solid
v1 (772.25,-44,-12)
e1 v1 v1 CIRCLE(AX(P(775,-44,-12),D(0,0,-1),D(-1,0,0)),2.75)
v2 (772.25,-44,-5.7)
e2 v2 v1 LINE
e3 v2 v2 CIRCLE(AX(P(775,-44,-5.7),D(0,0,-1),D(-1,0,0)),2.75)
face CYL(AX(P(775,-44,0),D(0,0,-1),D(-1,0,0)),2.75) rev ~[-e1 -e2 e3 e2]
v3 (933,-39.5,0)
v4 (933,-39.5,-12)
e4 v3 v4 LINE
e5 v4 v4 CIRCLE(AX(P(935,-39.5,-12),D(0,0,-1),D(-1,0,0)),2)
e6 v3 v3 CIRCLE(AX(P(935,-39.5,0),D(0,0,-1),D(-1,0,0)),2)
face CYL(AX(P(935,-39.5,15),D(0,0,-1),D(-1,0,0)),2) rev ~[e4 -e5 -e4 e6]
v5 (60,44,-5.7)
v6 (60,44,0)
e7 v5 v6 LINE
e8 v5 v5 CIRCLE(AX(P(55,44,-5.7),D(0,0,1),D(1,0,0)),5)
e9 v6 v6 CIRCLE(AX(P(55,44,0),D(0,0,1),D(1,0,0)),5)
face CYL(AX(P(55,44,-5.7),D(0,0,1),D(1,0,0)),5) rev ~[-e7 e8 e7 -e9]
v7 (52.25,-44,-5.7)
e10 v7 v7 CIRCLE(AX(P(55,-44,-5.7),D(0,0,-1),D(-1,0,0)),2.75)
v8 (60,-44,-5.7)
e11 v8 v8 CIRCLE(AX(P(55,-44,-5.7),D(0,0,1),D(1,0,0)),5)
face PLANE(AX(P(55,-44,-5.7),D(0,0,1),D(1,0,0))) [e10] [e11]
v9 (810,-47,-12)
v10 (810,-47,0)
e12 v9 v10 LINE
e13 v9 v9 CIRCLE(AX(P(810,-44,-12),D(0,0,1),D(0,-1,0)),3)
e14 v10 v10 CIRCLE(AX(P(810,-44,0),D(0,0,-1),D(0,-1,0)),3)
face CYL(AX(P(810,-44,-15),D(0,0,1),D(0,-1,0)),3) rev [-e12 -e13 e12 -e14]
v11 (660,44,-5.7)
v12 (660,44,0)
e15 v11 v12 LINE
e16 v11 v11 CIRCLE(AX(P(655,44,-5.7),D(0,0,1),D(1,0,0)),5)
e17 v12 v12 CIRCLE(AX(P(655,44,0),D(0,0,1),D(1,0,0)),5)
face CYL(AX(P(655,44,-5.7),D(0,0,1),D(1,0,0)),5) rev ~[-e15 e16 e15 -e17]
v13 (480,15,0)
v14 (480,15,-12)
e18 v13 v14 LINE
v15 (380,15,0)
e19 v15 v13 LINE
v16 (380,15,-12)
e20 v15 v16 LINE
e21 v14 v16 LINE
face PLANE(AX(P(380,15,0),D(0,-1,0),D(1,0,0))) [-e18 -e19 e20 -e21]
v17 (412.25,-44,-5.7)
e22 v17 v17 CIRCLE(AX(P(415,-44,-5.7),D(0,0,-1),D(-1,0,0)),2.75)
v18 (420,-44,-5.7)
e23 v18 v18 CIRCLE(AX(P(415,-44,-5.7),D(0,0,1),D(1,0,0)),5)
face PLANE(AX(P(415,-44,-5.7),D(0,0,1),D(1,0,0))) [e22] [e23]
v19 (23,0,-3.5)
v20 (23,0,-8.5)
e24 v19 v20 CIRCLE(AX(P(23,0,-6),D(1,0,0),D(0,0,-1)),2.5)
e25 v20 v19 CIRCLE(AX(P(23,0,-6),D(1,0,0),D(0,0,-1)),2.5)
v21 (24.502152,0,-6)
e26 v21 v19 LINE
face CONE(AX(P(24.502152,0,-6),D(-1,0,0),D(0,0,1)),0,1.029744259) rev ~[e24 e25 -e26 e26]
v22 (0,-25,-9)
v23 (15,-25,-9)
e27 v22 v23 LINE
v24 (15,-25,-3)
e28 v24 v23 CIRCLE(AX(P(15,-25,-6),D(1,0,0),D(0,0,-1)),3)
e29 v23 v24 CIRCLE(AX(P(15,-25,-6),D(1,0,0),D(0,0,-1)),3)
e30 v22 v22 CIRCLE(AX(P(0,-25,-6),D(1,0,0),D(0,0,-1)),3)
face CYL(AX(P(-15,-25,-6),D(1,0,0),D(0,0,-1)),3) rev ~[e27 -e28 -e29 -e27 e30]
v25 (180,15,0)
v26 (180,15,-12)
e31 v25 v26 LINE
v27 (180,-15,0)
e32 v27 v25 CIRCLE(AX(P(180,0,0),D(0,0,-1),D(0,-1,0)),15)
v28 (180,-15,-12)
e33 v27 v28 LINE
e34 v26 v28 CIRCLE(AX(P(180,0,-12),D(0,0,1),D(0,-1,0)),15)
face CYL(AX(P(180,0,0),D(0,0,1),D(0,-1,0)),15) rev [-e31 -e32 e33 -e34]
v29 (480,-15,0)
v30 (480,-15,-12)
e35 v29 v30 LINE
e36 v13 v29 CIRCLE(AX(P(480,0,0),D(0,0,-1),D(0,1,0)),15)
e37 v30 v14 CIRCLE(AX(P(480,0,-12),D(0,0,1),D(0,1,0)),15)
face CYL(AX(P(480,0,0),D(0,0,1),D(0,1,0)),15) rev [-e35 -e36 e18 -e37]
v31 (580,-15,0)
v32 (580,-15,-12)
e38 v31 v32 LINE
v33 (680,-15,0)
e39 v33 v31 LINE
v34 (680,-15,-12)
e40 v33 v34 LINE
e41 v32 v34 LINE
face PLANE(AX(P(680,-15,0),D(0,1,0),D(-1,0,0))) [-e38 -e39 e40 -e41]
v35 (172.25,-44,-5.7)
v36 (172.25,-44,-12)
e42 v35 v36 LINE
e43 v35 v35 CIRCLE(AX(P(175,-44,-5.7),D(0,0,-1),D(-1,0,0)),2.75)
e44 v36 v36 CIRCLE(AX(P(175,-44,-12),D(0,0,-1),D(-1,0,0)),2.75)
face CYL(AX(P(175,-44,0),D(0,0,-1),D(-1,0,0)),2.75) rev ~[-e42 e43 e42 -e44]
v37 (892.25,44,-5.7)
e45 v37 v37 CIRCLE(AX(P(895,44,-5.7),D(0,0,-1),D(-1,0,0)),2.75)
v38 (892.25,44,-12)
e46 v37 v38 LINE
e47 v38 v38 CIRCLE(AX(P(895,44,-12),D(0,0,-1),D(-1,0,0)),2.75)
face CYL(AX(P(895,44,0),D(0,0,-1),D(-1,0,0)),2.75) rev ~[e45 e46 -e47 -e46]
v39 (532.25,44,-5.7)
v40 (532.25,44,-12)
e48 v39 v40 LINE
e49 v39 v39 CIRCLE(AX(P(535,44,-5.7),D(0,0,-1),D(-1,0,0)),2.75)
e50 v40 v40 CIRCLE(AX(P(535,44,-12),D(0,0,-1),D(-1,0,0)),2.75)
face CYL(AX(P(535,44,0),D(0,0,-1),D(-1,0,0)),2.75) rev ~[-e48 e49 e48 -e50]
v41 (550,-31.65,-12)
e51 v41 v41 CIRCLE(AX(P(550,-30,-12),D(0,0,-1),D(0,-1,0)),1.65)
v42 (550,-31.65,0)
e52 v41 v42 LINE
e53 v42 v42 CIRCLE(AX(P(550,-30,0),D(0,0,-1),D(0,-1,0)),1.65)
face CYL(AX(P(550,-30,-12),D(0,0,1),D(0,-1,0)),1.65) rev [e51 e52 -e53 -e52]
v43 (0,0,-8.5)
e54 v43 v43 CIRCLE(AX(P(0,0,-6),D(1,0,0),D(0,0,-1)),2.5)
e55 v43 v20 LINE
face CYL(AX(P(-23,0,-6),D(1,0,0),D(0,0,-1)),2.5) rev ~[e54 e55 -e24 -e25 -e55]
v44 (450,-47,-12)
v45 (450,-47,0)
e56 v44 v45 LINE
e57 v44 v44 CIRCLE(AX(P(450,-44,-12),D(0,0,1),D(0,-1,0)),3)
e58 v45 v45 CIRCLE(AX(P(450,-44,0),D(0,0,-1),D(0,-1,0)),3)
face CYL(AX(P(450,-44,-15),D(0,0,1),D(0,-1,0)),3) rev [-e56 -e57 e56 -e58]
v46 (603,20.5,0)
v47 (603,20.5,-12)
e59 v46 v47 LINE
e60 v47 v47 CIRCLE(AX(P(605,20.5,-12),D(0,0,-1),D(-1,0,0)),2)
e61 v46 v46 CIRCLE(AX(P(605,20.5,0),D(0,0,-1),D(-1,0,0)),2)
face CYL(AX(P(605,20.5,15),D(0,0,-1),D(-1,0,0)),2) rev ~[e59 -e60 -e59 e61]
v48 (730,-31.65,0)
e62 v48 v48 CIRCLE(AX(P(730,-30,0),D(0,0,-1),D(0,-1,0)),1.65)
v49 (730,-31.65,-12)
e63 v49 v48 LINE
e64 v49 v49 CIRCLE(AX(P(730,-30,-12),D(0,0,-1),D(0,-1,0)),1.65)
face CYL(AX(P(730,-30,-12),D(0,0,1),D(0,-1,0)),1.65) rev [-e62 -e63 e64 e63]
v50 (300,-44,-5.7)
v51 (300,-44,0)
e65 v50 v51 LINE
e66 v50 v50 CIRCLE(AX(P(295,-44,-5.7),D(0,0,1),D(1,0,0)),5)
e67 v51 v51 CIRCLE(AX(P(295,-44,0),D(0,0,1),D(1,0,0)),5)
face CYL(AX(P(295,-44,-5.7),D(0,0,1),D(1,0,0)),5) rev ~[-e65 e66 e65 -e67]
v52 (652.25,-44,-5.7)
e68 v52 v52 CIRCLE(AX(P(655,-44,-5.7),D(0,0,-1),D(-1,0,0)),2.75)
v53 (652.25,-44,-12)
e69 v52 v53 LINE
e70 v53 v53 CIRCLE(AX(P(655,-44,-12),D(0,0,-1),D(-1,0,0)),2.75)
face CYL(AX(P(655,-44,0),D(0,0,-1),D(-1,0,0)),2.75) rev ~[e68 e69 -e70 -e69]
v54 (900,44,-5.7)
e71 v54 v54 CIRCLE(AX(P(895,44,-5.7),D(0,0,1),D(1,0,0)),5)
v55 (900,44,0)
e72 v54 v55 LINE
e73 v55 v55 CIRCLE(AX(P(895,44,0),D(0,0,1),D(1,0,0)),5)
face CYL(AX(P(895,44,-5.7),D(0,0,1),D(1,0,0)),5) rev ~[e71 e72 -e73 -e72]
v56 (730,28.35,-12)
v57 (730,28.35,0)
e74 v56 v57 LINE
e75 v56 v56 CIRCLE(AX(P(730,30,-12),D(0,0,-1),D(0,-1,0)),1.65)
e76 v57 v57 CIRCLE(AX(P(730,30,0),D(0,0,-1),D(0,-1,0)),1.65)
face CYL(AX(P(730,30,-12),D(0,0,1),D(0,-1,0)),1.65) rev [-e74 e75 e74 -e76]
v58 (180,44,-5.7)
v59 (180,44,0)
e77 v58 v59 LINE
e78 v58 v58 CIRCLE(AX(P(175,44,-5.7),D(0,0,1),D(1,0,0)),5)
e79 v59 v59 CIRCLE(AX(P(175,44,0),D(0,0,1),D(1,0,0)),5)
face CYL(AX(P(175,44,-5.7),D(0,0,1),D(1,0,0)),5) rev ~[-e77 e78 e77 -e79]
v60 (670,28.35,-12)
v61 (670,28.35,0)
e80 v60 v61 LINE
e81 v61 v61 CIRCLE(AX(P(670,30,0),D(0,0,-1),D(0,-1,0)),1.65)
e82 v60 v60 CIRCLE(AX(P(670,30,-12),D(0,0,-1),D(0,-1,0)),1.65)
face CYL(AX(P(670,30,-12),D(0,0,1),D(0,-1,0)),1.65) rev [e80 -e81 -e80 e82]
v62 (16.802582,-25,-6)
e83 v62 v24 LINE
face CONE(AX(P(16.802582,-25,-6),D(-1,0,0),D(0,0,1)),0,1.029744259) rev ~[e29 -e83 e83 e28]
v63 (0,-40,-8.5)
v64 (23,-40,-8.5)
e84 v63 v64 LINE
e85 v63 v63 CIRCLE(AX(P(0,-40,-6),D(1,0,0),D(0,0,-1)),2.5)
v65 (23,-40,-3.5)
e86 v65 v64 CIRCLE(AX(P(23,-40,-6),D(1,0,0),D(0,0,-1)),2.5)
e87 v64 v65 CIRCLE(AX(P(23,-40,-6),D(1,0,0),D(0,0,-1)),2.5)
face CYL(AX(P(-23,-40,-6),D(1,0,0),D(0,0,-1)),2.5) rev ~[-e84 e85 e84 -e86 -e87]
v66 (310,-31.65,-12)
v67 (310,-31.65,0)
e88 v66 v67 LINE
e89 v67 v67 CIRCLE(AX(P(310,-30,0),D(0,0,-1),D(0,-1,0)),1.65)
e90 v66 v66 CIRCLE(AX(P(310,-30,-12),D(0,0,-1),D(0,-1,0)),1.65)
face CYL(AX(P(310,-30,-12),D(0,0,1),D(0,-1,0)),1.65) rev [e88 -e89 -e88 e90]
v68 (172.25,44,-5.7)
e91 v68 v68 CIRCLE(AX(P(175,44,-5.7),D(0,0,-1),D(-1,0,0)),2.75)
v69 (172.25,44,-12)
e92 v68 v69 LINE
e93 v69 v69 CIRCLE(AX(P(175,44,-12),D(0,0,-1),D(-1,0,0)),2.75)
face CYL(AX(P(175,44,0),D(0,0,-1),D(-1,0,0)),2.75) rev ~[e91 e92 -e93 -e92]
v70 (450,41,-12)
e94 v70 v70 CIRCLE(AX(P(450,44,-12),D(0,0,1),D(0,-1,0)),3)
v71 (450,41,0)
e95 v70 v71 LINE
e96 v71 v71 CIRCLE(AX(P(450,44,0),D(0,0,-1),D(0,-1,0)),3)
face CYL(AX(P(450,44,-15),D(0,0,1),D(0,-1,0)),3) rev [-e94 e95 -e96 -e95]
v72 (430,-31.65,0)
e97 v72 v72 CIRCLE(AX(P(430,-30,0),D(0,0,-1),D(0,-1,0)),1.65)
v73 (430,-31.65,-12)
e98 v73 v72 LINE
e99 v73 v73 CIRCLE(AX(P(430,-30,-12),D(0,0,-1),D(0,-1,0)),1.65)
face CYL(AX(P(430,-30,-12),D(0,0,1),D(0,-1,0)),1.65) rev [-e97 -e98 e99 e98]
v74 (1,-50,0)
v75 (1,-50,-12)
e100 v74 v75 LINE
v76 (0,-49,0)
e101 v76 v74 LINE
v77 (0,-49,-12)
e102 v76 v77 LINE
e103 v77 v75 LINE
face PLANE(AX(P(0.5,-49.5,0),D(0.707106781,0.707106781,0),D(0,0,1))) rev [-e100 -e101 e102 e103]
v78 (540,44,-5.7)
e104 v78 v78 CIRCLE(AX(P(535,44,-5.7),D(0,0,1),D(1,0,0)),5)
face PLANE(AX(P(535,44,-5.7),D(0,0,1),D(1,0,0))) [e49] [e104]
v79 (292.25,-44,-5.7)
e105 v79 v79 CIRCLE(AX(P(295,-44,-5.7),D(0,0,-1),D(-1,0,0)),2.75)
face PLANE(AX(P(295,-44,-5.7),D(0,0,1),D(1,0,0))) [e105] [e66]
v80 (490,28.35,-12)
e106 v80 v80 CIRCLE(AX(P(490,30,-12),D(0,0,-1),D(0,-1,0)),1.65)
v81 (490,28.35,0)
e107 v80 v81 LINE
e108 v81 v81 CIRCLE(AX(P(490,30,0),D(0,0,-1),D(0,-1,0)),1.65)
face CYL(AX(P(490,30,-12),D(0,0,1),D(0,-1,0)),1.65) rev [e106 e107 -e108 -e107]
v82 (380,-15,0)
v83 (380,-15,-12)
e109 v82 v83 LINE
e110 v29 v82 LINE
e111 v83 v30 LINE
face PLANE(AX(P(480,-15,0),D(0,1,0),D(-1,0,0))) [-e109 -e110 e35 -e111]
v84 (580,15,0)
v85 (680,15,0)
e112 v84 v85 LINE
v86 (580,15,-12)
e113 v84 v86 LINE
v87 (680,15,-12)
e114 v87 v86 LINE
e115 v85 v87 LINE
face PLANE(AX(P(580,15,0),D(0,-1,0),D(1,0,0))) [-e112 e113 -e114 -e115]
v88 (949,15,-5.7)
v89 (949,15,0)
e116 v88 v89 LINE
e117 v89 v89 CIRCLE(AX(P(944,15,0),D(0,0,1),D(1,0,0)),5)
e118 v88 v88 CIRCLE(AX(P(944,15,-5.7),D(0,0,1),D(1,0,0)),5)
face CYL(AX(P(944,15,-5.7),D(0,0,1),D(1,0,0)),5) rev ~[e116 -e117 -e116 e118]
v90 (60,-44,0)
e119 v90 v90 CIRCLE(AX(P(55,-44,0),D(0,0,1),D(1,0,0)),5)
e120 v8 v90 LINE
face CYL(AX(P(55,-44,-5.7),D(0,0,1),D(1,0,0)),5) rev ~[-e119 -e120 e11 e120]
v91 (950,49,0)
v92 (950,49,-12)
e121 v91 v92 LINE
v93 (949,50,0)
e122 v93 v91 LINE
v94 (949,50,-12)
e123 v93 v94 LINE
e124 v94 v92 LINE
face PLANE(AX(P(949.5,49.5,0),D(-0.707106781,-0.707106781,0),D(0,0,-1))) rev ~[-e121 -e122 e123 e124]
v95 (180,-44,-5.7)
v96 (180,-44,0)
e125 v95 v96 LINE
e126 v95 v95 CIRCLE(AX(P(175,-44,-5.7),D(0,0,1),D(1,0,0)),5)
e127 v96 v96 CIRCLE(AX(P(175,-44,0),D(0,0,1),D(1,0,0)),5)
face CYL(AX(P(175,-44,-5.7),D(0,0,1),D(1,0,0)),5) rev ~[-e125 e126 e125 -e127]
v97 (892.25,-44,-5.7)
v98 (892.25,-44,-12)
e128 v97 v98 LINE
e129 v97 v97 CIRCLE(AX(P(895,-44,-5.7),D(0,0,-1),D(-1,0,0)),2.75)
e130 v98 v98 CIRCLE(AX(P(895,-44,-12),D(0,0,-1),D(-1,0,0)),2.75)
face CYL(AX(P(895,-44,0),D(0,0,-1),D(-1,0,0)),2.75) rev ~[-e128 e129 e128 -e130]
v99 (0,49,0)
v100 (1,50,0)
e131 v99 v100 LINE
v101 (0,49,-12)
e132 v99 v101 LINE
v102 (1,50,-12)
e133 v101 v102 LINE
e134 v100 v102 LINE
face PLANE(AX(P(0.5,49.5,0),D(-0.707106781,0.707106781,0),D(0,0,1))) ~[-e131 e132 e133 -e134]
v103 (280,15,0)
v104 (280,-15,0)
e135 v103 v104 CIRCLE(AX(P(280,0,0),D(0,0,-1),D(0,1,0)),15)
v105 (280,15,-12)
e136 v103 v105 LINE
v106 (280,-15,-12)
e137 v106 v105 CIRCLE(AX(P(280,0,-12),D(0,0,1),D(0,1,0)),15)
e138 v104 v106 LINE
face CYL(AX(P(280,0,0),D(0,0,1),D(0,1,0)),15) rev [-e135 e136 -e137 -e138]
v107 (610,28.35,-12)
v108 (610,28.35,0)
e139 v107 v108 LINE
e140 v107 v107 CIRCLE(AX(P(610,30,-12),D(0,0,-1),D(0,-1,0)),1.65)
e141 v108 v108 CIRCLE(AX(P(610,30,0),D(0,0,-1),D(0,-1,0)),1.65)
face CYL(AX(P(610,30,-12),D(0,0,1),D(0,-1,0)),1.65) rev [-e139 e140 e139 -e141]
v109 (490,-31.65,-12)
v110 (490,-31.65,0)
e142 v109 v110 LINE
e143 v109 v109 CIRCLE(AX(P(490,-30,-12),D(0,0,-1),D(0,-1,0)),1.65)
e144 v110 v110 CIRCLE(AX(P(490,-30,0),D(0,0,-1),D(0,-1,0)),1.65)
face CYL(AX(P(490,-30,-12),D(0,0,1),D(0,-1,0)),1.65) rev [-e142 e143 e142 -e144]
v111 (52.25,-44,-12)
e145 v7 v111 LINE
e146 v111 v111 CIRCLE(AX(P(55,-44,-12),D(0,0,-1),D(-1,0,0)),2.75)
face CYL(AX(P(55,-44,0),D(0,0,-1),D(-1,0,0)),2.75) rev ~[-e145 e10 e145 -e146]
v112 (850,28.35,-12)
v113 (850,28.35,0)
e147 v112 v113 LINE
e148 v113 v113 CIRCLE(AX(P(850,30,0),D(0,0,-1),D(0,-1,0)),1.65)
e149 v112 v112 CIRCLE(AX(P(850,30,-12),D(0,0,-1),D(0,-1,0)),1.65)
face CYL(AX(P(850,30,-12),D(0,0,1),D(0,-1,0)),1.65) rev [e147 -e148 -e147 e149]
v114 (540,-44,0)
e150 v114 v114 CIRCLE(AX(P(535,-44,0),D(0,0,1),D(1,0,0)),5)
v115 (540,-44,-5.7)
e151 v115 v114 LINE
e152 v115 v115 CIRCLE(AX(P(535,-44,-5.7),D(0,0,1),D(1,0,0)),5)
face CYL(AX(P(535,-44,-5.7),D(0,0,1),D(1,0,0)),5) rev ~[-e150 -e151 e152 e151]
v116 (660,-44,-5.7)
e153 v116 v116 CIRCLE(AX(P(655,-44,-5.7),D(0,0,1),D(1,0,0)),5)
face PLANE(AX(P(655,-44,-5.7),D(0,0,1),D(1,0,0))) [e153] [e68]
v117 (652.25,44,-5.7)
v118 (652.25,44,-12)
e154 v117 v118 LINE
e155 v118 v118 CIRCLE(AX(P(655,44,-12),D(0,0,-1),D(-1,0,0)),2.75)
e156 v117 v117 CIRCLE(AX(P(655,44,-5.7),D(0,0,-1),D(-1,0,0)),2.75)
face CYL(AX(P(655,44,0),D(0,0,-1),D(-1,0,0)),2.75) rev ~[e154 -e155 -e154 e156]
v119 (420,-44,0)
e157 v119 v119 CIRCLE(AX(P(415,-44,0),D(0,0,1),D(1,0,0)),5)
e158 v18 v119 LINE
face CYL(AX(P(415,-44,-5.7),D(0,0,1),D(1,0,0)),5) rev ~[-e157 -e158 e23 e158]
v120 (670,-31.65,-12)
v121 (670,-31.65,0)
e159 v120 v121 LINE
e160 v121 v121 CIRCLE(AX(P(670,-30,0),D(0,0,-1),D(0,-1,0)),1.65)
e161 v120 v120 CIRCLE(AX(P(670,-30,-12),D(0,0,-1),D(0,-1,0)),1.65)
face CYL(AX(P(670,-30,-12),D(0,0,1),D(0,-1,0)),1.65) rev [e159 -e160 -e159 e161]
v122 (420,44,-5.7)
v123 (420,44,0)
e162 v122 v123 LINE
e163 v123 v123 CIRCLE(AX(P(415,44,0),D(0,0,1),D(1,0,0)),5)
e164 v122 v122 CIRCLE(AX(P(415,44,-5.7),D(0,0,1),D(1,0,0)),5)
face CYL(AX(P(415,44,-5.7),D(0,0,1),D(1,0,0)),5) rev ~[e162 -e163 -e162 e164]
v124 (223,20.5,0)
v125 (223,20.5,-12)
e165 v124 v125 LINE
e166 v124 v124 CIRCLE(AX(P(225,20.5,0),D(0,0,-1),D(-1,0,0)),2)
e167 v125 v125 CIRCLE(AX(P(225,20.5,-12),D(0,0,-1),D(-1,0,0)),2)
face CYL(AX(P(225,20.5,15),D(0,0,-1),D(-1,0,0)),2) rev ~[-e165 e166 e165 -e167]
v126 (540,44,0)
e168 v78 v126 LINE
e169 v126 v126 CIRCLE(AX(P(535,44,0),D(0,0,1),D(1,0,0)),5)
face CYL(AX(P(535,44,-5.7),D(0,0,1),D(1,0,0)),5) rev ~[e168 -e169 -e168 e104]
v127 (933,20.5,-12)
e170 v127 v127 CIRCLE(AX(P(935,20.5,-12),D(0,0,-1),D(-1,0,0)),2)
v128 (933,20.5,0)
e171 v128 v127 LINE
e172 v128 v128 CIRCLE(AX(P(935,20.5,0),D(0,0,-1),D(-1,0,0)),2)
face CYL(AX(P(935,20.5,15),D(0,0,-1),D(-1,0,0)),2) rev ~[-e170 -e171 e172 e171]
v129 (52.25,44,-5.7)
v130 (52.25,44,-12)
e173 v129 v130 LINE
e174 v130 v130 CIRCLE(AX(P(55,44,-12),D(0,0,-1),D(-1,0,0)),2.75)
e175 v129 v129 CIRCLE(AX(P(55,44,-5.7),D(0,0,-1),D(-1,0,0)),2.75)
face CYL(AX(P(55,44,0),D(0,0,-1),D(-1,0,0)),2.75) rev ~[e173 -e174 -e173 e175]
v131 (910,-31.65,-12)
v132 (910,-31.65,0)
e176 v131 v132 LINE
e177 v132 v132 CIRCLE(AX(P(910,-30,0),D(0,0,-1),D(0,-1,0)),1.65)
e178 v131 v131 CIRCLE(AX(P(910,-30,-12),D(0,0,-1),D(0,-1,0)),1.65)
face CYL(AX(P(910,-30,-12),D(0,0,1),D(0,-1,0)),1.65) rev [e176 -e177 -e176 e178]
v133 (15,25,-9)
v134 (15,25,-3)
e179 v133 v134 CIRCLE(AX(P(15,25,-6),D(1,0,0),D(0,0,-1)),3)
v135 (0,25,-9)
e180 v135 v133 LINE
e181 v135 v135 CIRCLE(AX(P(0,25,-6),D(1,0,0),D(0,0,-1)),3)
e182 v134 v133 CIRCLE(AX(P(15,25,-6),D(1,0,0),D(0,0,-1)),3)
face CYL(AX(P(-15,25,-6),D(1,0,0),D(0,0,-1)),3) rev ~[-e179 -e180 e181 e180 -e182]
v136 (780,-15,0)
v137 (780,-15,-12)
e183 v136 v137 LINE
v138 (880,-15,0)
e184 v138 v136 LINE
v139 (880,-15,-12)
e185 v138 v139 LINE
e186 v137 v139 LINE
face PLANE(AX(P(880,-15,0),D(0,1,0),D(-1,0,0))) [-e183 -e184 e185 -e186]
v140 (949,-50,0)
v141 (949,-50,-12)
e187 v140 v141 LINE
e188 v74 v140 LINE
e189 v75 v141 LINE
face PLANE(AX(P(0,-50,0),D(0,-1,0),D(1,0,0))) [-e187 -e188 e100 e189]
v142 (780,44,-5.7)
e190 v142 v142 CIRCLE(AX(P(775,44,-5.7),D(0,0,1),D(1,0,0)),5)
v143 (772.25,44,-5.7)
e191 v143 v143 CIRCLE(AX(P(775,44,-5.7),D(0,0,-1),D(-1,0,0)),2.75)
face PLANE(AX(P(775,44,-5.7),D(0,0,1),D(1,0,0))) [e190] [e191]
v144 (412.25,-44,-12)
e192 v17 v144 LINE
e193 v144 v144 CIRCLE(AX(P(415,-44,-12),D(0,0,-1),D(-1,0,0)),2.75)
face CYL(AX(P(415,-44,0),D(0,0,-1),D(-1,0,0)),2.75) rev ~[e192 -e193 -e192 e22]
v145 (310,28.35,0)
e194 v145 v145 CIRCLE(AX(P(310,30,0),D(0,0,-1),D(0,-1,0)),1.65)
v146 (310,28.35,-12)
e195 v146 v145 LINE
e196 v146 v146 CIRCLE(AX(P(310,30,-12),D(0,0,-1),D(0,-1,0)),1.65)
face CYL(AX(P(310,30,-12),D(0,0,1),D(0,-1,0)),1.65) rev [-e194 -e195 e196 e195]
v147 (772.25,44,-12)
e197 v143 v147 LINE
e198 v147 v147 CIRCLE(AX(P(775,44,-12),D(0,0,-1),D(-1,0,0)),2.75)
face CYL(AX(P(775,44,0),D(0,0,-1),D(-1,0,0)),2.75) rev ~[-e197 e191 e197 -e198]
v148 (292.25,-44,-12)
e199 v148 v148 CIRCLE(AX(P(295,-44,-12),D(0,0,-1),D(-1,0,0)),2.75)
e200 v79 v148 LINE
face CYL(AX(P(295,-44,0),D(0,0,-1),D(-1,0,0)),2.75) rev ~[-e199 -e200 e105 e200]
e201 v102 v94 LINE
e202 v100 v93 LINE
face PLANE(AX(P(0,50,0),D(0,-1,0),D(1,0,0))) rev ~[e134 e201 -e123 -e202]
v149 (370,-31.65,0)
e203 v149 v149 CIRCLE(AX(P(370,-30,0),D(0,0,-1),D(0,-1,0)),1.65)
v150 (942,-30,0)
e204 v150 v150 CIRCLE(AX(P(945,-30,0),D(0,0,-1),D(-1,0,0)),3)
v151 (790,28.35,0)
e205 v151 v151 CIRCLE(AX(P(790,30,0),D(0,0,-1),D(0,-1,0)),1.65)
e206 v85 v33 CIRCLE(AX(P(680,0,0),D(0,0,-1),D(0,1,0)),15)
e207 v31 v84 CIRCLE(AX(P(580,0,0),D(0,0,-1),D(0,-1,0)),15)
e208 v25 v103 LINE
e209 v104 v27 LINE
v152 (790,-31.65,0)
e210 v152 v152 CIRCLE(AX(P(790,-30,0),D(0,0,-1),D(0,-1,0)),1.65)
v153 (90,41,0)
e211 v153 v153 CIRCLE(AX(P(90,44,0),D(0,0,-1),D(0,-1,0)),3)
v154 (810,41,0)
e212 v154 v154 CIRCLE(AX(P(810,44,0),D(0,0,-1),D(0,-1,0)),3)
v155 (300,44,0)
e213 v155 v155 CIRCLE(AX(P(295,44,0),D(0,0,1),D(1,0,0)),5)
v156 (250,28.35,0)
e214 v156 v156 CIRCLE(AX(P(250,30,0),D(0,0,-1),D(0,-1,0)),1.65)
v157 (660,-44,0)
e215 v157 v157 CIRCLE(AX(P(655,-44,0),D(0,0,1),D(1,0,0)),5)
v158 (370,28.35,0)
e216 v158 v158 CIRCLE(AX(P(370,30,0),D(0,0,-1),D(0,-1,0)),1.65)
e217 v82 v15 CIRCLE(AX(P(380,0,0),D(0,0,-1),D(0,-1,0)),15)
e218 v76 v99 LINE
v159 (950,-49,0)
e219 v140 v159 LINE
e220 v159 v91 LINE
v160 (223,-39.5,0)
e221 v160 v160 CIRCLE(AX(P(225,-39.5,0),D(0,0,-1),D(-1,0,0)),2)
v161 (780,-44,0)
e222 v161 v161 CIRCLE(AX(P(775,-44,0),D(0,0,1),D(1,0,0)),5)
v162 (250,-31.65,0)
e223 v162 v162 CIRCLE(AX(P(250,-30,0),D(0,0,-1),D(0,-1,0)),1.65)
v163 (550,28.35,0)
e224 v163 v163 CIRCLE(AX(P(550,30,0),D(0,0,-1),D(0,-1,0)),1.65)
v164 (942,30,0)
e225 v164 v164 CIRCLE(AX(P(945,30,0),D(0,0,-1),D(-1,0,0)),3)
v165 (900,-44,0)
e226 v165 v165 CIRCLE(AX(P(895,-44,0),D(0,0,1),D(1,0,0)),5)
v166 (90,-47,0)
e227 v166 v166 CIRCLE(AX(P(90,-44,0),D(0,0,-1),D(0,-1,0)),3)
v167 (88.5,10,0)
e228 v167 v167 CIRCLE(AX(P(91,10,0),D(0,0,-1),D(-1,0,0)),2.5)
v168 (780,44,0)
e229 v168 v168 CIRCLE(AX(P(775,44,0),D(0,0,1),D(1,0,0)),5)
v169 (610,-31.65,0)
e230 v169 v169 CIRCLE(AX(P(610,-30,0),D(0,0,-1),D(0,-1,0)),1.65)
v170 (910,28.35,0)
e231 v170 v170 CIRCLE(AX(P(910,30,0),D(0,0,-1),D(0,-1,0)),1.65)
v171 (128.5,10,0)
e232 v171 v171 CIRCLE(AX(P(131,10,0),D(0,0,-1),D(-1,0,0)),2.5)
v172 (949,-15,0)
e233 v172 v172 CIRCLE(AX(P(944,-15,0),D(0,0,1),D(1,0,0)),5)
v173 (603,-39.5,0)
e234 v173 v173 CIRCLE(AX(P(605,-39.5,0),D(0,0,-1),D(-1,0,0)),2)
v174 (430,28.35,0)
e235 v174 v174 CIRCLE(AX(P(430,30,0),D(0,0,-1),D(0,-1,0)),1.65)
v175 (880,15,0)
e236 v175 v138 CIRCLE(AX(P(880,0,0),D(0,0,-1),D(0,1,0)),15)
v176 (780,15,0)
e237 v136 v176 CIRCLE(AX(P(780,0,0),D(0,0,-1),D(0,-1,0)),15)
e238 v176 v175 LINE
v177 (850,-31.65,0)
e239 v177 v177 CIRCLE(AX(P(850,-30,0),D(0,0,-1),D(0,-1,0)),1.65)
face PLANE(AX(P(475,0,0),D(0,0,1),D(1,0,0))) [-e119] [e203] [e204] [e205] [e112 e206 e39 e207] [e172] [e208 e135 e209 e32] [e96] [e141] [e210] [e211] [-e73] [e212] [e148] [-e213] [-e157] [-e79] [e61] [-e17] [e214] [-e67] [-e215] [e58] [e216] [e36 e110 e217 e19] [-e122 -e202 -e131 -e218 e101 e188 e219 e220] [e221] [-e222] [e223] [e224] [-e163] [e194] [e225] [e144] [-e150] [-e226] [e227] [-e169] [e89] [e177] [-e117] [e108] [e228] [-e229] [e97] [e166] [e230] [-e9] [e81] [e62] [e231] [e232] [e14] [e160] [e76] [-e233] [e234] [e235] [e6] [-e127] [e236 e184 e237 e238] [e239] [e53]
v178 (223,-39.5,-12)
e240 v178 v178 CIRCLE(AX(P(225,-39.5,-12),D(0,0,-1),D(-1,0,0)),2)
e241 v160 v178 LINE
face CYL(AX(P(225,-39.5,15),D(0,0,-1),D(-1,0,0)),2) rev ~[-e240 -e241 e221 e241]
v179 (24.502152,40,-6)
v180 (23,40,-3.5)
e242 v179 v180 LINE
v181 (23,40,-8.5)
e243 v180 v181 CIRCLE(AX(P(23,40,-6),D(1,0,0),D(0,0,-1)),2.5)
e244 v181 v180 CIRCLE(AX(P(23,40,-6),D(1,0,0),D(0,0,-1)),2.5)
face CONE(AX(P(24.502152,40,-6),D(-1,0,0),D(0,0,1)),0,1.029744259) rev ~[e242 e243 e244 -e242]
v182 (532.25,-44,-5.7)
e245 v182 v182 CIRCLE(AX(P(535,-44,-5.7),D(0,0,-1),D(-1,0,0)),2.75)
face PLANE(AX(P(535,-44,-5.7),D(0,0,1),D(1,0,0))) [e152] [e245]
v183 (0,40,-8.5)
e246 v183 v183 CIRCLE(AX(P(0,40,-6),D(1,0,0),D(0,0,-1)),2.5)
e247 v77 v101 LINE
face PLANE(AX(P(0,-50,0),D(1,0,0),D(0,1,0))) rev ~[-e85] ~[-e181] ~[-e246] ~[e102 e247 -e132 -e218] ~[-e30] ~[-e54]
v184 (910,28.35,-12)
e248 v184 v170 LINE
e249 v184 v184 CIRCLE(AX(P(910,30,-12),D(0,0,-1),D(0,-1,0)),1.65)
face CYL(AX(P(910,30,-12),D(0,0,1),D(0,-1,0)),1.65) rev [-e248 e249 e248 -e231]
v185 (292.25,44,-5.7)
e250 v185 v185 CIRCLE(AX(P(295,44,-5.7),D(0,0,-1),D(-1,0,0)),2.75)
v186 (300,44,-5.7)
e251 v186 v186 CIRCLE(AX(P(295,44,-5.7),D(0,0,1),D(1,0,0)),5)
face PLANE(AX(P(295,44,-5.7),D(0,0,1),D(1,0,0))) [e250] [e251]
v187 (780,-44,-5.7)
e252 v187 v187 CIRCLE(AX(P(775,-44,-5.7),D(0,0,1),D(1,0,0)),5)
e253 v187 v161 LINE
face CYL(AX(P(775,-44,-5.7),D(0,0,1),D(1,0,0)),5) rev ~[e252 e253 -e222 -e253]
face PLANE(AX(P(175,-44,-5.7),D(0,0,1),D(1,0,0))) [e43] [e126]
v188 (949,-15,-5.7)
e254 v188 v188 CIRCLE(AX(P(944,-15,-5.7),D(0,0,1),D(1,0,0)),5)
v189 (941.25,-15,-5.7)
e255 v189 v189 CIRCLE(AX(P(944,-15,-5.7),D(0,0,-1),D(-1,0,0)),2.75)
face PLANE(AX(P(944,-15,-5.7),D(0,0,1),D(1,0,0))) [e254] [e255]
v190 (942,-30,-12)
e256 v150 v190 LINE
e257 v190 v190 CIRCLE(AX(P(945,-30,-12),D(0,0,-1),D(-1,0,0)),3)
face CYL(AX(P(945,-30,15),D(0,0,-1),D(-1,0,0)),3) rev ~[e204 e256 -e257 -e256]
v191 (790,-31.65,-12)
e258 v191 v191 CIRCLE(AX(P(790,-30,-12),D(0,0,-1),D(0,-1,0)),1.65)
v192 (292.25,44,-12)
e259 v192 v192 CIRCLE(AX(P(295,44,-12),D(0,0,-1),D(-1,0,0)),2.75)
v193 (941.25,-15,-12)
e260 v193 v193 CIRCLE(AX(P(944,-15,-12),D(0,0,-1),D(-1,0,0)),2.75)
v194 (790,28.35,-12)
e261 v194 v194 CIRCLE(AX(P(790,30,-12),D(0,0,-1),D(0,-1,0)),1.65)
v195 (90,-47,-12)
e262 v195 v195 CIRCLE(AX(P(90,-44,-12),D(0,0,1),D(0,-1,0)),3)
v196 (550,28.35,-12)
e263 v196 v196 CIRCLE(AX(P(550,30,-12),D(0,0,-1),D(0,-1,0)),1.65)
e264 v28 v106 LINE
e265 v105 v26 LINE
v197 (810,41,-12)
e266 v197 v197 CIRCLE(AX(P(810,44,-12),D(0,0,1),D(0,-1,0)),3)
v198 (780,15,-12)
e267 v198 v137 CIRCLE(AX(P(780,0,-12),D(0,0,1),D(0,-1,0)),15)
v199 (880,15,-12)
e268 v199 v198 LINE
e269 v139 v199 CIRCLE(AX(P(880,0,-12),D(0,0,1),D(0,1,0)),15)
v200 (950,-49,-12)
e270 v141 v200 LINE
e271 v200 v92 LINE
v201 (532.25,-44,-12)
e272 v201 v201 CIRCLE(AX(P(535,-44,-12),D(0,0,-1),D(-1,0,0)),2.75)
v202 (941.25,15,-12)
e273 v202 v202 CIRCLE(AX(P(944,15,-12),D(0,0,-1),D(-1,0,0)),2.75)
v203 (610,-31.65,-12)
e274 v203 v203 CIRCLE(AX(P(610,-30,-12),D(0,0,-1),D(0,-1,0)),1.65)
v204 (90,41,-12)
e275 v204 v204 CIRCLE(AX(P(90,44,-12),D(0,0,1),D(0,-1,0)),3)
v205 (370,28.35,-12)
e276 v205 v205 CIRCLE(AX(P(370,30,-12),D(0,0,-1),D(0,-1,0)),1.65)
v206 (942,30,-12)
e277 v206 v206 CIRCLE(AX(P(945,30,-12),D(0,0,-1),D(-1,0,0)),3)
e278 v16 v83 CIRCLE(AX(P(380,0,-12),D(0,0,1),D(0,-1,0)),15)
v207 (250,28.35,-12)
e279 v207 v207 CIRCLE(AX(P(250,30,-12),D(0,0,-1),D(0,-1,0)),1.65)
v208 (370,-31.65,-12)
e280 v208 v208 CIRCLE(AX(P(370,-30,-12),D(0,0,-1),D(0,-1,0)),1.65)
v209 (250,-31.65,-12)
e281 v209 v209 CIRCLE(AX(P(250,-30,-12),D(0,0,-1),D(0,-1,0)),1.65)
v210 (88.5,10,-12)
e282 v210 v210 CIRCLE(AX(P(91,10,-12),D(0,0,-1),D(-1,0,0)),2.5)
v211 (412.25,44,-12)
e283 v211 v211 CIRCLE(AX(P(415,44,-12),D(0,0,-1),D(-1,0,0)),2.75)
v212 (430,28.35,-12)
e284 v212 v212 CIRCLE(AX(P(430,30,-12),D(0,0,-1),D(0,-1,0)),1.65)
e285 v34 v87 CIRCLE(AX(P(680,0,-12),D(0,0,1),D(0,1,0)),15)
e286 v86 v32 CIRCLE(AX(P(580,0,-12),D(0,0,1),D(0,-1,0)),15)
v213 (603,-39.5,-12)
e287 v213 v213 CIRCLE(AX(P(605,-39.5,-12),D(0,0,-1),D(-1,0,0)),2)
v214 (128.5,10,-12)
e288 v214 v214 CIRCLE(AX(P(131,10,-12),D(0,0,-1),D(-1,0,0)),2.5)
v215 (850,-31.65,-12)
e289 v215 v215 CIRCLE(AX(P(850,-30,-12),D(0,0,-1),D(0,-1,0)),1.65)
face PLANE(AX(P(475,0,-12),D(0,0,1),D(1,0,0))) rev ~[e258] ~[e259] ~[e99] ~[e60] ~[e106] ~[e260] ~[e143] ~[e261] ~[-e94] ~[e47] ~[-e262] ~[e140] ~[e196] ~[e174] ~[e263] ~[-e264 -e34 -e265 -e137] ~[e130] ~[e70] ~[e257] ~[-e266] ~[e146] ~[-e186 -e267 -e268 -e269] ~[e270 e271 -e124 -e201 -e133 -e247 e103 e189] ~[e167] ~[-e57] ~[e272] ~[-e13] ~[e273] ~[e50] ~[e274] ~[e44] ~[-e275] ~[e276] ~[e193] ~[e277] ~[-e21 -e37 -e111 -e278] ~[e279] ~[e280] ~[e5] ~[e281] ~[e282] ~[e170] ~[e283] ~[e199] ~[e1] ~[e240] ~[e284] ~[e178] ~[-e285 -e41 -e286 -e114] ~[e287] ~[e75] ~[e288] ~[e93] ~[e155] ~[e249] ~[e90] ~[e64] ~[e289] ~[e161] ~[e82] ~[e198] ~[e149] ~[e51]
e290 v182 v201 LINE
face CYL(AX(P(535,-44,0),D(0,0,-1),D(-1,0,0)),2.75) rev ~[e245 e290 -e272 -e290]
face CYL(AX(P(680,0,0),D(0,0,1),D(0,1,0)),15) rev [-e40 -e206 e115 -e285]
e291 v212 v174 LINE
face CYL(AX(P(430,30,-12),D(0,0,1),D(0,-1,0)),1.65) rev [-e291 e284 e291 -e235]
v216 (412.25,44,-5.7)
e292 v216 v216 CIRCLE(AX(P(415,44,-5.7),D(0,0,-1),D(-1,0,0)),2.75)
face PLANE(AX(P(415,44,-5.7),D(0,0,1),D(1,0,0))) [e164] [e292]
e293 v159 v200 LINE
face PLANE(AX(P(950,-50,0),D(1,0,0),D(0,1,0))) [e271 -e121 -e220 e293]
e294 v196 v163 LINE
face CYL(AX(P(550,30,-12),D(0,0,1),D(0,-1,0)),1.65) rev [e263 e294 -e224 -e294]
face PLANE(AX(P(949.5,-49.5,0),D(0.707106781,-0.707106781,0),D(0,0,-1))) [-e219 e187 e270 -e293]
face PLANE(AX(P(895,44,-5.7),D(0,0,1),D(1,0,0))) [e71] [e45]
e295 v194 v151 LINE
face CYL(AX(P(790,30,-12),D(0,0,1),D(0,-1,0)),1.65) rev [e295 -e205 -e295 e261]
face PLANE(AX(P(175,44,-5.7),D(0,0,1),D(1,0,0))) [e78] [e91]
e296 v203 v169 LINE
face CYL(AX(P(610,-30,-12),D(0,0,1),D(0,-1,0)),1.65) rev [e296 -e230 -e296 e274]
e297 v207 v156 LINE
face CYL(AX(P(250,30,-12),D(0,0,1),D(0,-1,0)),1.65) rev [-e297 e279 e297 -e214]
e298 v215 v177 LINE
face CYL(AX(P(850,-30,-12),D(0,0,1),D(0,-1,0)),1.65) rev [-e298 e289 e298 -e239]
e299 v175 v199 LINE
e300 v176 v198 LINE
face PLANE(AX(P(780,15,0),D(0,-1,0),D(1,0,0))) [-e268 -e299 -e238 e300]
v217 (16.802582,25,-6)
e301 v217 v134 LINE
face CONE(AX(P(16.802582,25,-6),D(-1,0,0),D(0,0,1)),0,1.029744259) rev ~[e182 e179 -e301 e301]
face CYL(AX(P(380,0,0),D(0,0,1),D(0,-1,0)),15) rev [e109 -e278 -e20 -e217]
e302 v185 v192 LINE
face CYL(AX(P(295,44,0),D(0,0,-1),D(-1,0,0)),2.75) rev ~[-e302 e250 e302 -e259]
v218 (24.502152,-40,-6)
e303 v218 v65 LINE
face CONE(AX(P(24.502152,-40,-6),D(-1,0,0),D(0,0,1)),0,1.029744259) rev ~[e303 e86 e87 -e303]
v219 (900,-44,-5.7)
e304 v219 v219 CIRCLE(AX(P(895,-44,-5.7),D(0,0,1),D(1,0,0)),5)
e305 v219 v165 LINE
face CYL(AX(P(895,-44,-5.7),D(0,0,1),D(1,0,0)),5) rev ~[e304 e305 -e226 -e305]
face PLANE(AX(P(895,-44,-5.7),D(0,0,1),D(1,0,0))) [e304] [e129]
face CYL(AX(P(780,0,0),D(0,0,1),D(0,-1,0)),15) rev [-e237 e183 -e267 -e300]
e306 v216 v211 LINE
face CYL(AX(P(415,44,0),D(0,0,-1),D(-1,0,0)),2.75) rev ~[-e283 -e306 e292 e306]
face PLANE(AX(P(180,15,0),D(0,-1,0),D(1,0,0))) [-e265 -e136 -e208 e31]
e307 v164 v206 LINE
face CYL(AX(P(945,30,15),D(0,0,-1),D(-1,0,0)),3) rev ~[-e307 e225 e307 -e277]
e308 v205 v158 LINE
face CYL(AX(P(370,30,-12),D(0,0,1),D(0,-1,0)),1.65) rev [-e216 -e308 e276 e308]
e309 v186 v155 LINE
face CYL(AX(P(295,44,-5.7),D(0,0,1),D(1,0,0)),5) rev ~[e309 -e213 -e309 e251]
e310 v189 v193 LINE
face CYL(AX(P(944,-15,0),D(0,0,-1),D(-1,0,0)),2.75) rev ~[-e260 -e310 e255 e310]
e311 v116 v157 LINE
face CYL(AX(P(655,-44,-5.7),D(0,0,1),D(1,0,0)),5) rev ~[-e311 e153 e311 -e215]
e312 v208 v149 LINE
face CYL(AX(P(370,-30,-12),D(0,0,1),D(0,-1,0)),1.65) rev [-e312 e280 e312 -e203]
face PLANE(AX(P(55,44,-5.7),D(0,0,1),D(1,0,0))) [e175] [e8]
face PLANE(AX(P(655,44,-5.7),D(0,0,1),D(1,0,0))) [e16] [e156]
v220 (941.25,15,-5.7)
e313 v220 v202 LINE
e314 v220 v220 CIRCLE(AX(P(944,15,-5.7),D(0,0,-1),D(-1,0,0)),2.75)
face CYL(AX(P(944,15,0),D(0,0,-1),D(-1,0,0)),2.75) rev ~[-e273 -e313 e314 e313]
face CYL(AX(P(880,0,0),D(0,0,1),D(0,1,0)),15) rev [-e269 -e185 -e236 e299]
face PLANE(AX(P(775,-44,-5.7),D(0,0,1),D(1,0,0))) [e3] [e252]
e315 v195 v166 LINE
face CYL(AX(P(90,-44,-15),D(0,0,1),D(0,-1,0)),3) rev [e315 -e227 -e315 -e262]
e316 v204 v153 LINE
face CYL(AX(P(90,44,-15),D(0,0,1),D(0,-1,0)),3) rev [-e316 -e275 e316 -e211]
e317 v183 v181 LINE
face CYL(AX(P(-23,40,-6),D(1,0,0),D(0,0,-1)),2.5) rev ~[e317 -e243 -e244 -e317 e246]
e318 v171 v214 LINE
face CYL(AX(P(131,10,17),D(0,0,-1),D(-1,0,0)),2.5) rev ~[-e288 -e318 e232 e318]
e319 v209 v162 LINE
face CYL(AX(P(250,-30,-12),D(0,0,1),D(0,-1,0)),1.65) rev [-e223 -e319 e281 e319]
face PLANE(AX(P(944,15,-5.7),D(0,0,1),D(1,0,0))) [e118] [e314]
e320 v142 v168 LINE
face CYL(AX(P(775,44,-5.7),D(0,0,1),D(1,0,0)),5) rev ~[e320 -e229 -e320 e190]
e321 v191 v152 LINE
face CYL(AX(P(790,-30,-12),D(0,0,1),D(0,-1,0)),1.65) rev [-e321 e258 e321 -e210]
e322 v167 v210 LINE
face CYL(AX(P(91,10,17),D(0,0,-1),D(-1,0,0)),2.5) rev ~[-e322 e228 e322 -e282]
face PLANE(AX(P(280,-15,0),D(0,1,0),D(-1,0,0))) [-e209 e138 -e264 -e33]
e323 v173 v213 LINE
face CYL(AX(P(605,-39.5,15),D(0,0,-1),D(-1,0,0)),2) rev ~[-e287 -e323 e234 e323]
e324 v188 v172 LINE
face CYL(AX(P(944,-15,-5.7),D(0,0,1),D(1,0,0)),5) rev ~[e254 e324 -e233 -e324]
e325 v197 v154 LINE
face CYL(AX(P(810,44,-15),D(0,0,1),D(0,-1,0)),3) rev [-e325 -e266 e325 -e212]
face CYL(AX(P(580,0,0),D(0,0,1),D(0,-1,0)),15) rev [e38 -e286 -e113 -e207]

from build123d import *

# Parameters (mm, degrees)
SKETCH1_W                                        = 950
SKETCH1_H                                        = 100
BOSS_EXTRUDE1_DEPTH                              = 12
CUT_EXTRUDE1_REACH                               = 953.391
M4_TAPPED_HOLE1_AT_2_COUNT                       = 2
M4_TAPPED_HOLE1_AT_2_PITCH                       = 60
LPATTERN1_COUNT                                  = 12
LPATTERN1_PITCH                                  = 60
F_6_0_6_DIAMETER_HOLE1_D                         = 6
F_6_0_6_DIAMETER_HOLE1_DEPTH                     = 15
F_6_0_6_DIAMETER_HOLE1_TIP                       = 1.802581857
F_4_0_4_DIAMETER_HOLE1_D                         = 4
F_4_0_4_DIAMETER_HOLE1_DEPTH                     = 15
F_4_0_4_DIAMETER_HOLE1_TIP                       = 1.201721238
M6_TAPPED_HOLE1_D                                = 5
M6_TAPPED_HOLE1_DEPTH                            = 23
M6_TAPPED_HOLE1_TIP                              = 1.502151548
F_6_0_6_DIAMETER_HOLE2_D                         = 6
F_6_0_6_DIAMETER_HOLE2_DEPTH                     = 15
F_6_0_6_DIAMETER_HOLE2_TIP                       = 1.802581857
HOLE_SIZE_PER_HEX_SOCKET_SCREW_TYPE1_D           = 5.5
HOLE_SIZE_PER_HEX_SOCKET_SCREW_TYPE1_CBORE_D     = 10
HOLE_SIZE_PER_HEX_SOCKET_SCREW_TYPE1_CBORE_DEPTH = 5.7
LPATTERN2_COUNT                                  = 8
LPATTERN2_PITCH                                  = 120
F_6_0_6_DIAMETER_HOLE3_AT_2_COUNT                = 2
F_6_0_6_DIAMETER_HOLE3_AT_2_PITCH                = 88
LPATTERN3_COUNT                                  = 3
LPATTERN3_PITCH                                  = 360
HOLE_SIZE_PER_HEX_SOCKET_SCREW_TYPE2_D           = 5.5
HOLE_SIZE_PER_HEX_SOCKET_SCREW_TYPE2_CBORE_D     = 10
HOLE_SIZE_PER_HEX_SOCKET_SCREW_TYPE2_CBORE_DEPTH = 5.7
M6_TAPPED_HOLE2_D                                = 5
M6_TAPPED_HOLE2_DEPTH                            = 17
M6_TAPPED_HOLE2_TIP                              = 1.502151548
CHAMFER1_SIZE                                    = 1


with BuildPart() as part:
    # Sketch1 → Boss-Extrude1 (new body)
    with BuildSketch(Plane.XY):
        with Locations((475, 0)):
            Rectangle(SKETCH1_W, SKETCH1_H)
    extrude(amount=-BOSS_EXTRUDE1_DEPTH)

    # Sketch7 → Cut-Extrude1 (cut, up to next)
    with BuildSketch(Plane.XY, mode=Mode.PRIVATE) as cut_extrude1_sk1:
        with BuildLine():
            Line((180, 15), (280, 15))
            ThreePointArc((280, 15), (295, 0), (280, -15))
            Line((280, -15), (180, -15))
            ThreePointArc((180, -15), (165, 0), (180, 15))
        make_face()
    cut_extrude1_tool1 = extrude(cut_extrude1_sk1.sketch, amount=-CUT_EXTRUDE1_REACH, mode=Mode.PRIVATE) & part.part
    # Sketch7 → Cut-Extrude1 (cut, up to next)
    with BuildSketch(Plane.XY, mode=Mode.PRIVATE) as cut_extrude1_sk2:
        with BuildLine():
            Line((380, 15), (480, 15))
            ThreePointArc((480, 15), (495, 0), (480, -15))
            Line((480, -15), (380, -15))
            ThreePointArc((380, -15), (365, 0), (380, 15))
        make_face()
    cut_extrude1_tool2 = extrude(cut_extrude1_sk2.sketch, amount=-CUT_EXTRUDE1_REACH, mode=Mode.PRIVATE) & part.part
    # Sketch7 → Cut-Extrude1 (cut, up to next)
    with BuildSketch(Plane.XY, mode=Mode.PRIVATE) as cut_extrude1_sk3:
        with BuildLine():
            Line((580, 15), (680, 15))
            ThreePointArc((680, 15), (695, 0), (680, -15))
            Line((680, -15), (580, -15))
            ThreePointArc((580, -15), (565, 0), (580, 15))
        make_face()
    cut_extrude1_tool3 = extrude(cut_extrude1_sk3.sketch, amount=-CUT_EXTRUDE1_REACH, mode=Mode.PRIVATE) & part.part
    # Sketch7 → Cut-Extrude1 (cut, up to next)
    with BuildSketch(Plane.XY, mode=Mode.PRIVATE) as cut_extrude1_sk4:
        with BuildLine():
            Line((780, 15), (880, 15))
            ThreePointArc((880, 15), (895, 0), (880, -15))
            Line((880, -15), (780, -15))
            ThreePointArc((780, -15), (765, 0), (780, 15))
        make_face()
    cut_extrude1_tool4 = extrude(cut_extrude1_sk4.sketch, amount=-CUT_EXTRUDE1_REACH, mode=Mode.PRIVATE) & part.part
    add(cut_extrude1_tool1.solids().sort_by_distance((230, 0, 0))[0], mode=Mode.SUBTRACT)
    add(cut_extrude1_tool2.solids().sort_by_distance((430, 0, 0))[0], mode=Mode.SUBTRACT)
    add(cut_extrude1_tool3.solids().sort_by_distance((630, 0, 0))[0], mode=Mode.SUBTRACT)
    add(cut_extrude1_tool4.solids().sort_by_distance((830, 0, 0))[0], mode=Mode.SUBTRACT)

    # Sketch11 → M4 Tapped Hole1 (revolve, cut)
    with BuildSketch(Plane(origin=(250, 30, 0), x_dir=(0, -1, 0), z_dir=(1, 0, 0))):
        Polygon((0, 0), (0, 12.991420021), (1.65, 12), (1.65, 0), align=None)
    m4_tapped_hole1 = revolve(axis=Axis((250, 30, 6.35), (0, 0, -1)), mode=Mode.SUBTRACT)

    # M4 Tapped Hole1 at 2: M4 Tapped Hole1 ×2
    with Locations(*[(0, -i * M4_TAPPED_HOLE1_AT_2_PITCH, 0) for i in range(1, M4_TAPPED_HOLE1_AT_2_COUNT)]):
        add(m4_tapped_hole1, mode=Mode.SUBTRACT)

    # LPattern1: M4 Tapped Hole1 ×12
    with Locations(*[(i * LPATTERN1_PITCH, 0, 0) for i in range(1, LPATTERN1_COUNT)]):
        add(m4_tapped_hole1, mode=Mode.SUBTRACT)

    # LPattern1 copy 1 sketch → LPattern1 copy 1 (revolve, cut)
    with BuildSketch(Plane(origin=(310, -30, 0), x_dir=(0, -1, 0), z_dir=(1, 0, 0))):
        Polygon((0, 0), (0, 12.991420021), (1.65, 12), (1.65, 0), align=None)
    revolve(axis=Axis((310, -30, 6.35), (0, 0, -1)), mode=Mode.SUBTRACT)

    # LPattern1 copy 2 sketch → LPattern1 copy 2 (revolve, cut)
    with BuildSketch(Plane(origin=(370, -30, 0), x_dir=(0, -1, 0), z_dir=(1, 0, 0))):
        Polygon((0, 0), (0, 12.991420021), (1.65, 12), (1.65, 0), align=None)
    revolve(axis=Axis((370, -30, 6.35), (0, 0, -1)), mode=Mode.SUBTRACT)

    # LPattern1 copy 3 sketch → LPattern1 copy 3 (revolve, cut)
    with BuildSketch(Plane(origin=(430, -30, 0), x_dir=(0, -1, 0), z_dir=(1, 0, 0))):
        Polygon((0, 0), (0, 12.991420021), (1.65, 12), (1.65, 0), align=None)
    revolve(axis=Axis((430, -30, 6.35), (0, 0, -1)), mode=Mode.SUBTRACT)

    # LPattern1 copy 4 sketch → LPattern1 copy 4 (revolve, cut)
    with BuildSketch(Plane(origin=(490, -30, 0), x_dir=(0, -1, 0), z_dir=(1, 0, 0))):
        Polygon((0, 0), (0, 12.991420021), (1.65, 12), (1.65, 0), align=None)
    revolve(axis=Axis((490, -30, 6.35), (0, 0, -1)), mode=Mode.SUBTRACT)

    # LPattern1 copy 5 sketch → LPattern1 copy 5 (revolve, cut)
    with BuildSketch(Plane(origin=(550, -30, 0), x_dir=(0, -1, 0), z_dir=(1, 0, 0))):
        Polygon((0, 0), (0, 12.991420021), (1.65, 12), (1.65, 0), align=None)
    revolve(axis=Axis((550, -30, 6.35), (0, 0, -1)), mode=Mode.SUBTRACT)

    # LPattern1 copy 6 sketch → LPattern1 copy 6 (revolve, cut)
    with BuildSketch(Plane(origin=(610, -30, 0), x_dir=(0, -1, 0), z_dir=(1, 0, 0))):
        Polygon((0, 0), (0, 12.991420021), (1.65, 12), (1.65, 0), align=None)
    revolve(axis=Axis((610, -30, 6.35), (0, 0, -1)), mode=Mode.SUBTRACT)

    # LPattern1 copy 7 sketch → LPattern1 copy 7 (revolve, cut)
    with BuildSketch(Plane(origin=(670, -30, 0), x_dir=(0, -1, 0), z_dir=(1, 0, 0))):
        Polygon((0, 0), (0, 12.991420021), (1.65, 12), (1.65, 0), align=None)
    revolve(axis=Axis((670, -30, 6.35), (0, 0, -1)), mode=Mode.SUBTRACT)

    # LPattern1 copy 8 sketch → LPattern1 copy 8 (revolve, cut)
    with BuildSketch(Plane(origin=(730, -30, 0), x_dir=(0, -1, 0), z_dir=(1, 0, 0))):
        Polygon((0, 0), (0, 12.991420021), (1.65, 12), (1.65, 0), align=None)
    revolve(axis=Axis((730, -30, 6.35), (0, 0, -1)), mode=Mode.SUBTRACT)

    # LPattern1 copy 9 sketch → LPattern1 copy 9 (revolve, cut)
    with BuildSketch(Plane(origin=(790, -30, 0), x_dir=(0, -1, 0), z_dir=(1, 0, 0))):
        Polygon((0, 0), (0, 12.991420021), (1.65, 12), (1.65, 0), align=None)
    revolve(axis=Axis((790, -30, 6.35), (0, 0, -1)), mode=Mode.SUBTRACT)

    # LPattern1 copy 10 sketch → LPattern1 copy 10 (revolve, cut)
    with BuildSketch(Plane(origin=(850, -30, 0), x_dir=(0, -1, 0), z_dir=(1, 0, 0))):
        Polygon((0, 0), (0, 12.991420021), (1.65, 12), (1.65, 0), align=None)
    revolve(axis=Axis((850, -30, 6.35), (0, 0, -1)), mode=Mode.SUBTRACT)

    # LPattern1 copy 11 sketch → LPattern1 copy 11 (revolve, cut)
    with BuildSketch(Plane(origin=(910, -30, 0), x_dir=(0, -1, 0), z_dir=(1, 0, 0))):
        Polygon((0, 0), (0, 12.991420021), (1.65, 12), (1.65, 0), align=None)
    revolve(axis=Axis((910, -30, 6.35), (0, 0, -1)), mode=Mode.SUBTRACT)

    # Ø6.0 (6) Diameter Hole1
    with Locations(Plane.XY):
        with Locations((945, 30), (945, -30)):
            Hole(F_6_0_6_DIAMETER_HOLE1_D / 2, depth=F_6_0_6_DIAMETER_HOLE1_DEPTH)
            with Locations((0, 0, -(F_6_0_6_DIAMETER_HOLE1_DEPTH + F_6_0_6_DIAMETER_HOLE1_TIP / 2))):  # 118° drill point
                Cone(0, F_6_0_6_DIAMETER_HOLE1_D / 2, F_6_0_6_DIAMETER_HOLE1_TIP, mode=Mode.SUBTRACT)

    # Ø4.0 (4) Diameter Hole1
    with Locations(Plane.XY):
        with Locations((225, -39.5), (605, -39.5), (935, -39.5), (225, 20.5), (605, 20.5), (935, 20.5)):
            Hole(F_4_0_4_DIAMETER_HOLE1_D / 2, depth=F_4_0_4_DIAMETER_HOLE1_DEPTH)
            with Locations((0, 0, -(F_4_0_4_DIAMETER_HOLE1_DEPTH + F_4_0_4_DIAMETER_HOLE1_TIP / 2))):  # 118° drill point
                Cone(0, F_4_0_4_DIAMETER_HOLE1_D / 2, F_4_0_4_DIAMETER_HOLE1_TIP, mode=Mode.SUBTRACT)

    # M6 Tapped Hole1
    with Locations(Plane.ZY):
        with Locations((-6, 0), (-6, 40), (-6, -40)):
            Hole(M6_TAPPED_HOLE1_D / 2, depth=M6_TAPPED_HOLE1_DEPTH)
            with Locations((0, 0, -(M6_TAPPED_HOLE1_DEPTH + M6_TAPPED_HOLE1_TIP / 2))):  # 118° drill point
                Cone(0, M6_TAPPED_HOLE1_D / 2, M6_TAPPED_HOLE1_TIP, mode=Mode.SUBTRACT)

    # Ø6.0 (6) Diameter Hole2
    with Locations(Plane.ZY):
        with Locations((-6, 25), (-6, -25)):
            Hole(F_6_0_6_DIAMETER_HOLE2_D / 2, depth=F_6_0_6_DIAMETER_HOLE2_DEPTH)
            with Locations((0, 0, -(F_6_0_6_DIAMETER_HOLE2_DEPTH + F_6_0_6_DIAMETER_HOLE2_TIP / 2))):  # 118° drill point
                Cone(0, F_6_0_6_DIAMETER_HOLE2_D / 2, F_6_0_6_DIAMETER_HOLE2_TIP, mode=Mode.SUBTRACT)

    # Hole size per hex socket screw type1 (through all)
    with Locations(Plane.XY):
        with Locations((55, -44), (55, 44)):
            hole_size_per_hex_socket_screw_type1 = CounterBoreHole(HOLE_SIZE_PER_HEX_SOCKET_SCREW_TYPE1_D / 2, HOLE_SIZE_PER_HEX_SOCKET_SCREW_TYPE1_CBORE_D / 2, HOLE_SIZE_PER_HEX_SOCKET_SCREW_TYPE1_CBORE_DEPTH)

    # LPattern2: Hole size per hex socket screw type1 ×8
    with Locations(*[(i * LPATTERN2_PITCH, 0, 0) for i in range(1, LPATTERN2_COUNT)]):
        add(hole_size_per_hex_socket_screw_type1, mode=Mode.SUBTRACT)

    # Sketch30 → Ø6.0 (6) Diameter Hole3 (revolve, cut)
    with BuildSketch(Plane(origin=(90, -44, 0), x_dir=(0, -1, 0), z_dir=(1, 0, 0))):
        Polygon((0, 0), (0, 16.802581857), (3, 15), (3, 0), align=None)
    f_6_0_6_diameter_hole3 = revolve(axis=Axis((90, -44, 6.35), (0, 0, -1)), mode=Mode.SUBTRACT)

    # Ø6.0 (6) Diameter Hole3 at 2: Ø6.0 (6) Diameter Hole3 ×2
    with Locations(*[(0, i * F_6_0_6_DIAMETER_HOLE3_AT_2_PITCH, 0) for i in range(1, F_6_0_6_DIAMETER_HOLE3_AT_2_COUNT)]):
        add(f_6_0_6_diameter_hole3, mode=Mode.SUBTRACT)

    # LPattern3: Ø6.0 (6) Diameter Hole3 ×3
    with Locations(*[(i * LPATTERN3_PITCH, 0, 0) for i in range(1, LPATTERN3_COUNT)]):
        add(f_6_0_6_diameter_hole3, mode=Mode.SUBTRACT)

    # LPattern3 copy 1 sketch → LPattern3 copy 1 (revolve, cut)
    with BuildSketch(Plane(origin=(450, 44, 0), x_dir=(0, -1, 0), z_dir=(1, 0, 0))):
        Polygon((0, 0), (0, 16.802581857), (3, 15), (3, 0), align=None)
    revolve(axis=Axis((450, 44, 6.35), (0, 0, -1)), mode=Mode.SUBTRACT)

    # LPattern3 copy 2 sketch → LPattern3 copy 2 (revolve, cut)
    with BuildSketch(Plane(origin=(810, 44, 0), x_dir=(0, -1, 0), z_dir=(1, 0, 0))):
        Polygon((0, 0), (0, 16.802581857), (3, 15), (3, 0), align=None)
    revolve(axis=Axis((810, 44, 6.35), (0, 0, -1)), mode=Mode.SUBTRACT)

    # Hole size per hex socket screw type2 (through all)
    with Locations(Plane.XY):
        with Locations((944, 15), (944, -15)):
            CounterBoreHole(HOLE_SIZE_PER_HEX_SOCKET_SCREW_TYPE2_D / 2, HOLE_SIZE_PER_HEX_SOCKET_SCREW_TYPE2_CBORE_D / 2, HOLE_SIZE_PER_HEX_SOCKET_SCREW_TYPE2_CBORE_DEPTH)

    # M6 Tapped Hole2
    with Locations(Plane.XY):
        with Locations((91, 10), (131, 10)):
            Hole(M6_TAPPED_HOLE2_D / 2, depth=M6_TAPPED_HOLE2_DEPTH)
            with Locations((0, 0, -(M6_TAPPED_HOLE2_DEPTH + M6_TAPPED_HOLE2_TIP / 2))):  # 118° drill point
                Cone(0, M6_TAPPED_HOLE2_D / 2, M6_TAPPED_HOLE2_TIP, mode=Mode.SUBTRACT)

    # Chamfer1
    chamfer1_edges = [part.edges().sort_by_distance(p)[0] for p in [
        (950, -50, -6),
        (0, -50, -6),
        (0, 50, -6),
        (950, 50, -6),
    ]]
    chamfer(chamfer1_edges, length=CHAMFER1_SIZE)


solid = part.part
